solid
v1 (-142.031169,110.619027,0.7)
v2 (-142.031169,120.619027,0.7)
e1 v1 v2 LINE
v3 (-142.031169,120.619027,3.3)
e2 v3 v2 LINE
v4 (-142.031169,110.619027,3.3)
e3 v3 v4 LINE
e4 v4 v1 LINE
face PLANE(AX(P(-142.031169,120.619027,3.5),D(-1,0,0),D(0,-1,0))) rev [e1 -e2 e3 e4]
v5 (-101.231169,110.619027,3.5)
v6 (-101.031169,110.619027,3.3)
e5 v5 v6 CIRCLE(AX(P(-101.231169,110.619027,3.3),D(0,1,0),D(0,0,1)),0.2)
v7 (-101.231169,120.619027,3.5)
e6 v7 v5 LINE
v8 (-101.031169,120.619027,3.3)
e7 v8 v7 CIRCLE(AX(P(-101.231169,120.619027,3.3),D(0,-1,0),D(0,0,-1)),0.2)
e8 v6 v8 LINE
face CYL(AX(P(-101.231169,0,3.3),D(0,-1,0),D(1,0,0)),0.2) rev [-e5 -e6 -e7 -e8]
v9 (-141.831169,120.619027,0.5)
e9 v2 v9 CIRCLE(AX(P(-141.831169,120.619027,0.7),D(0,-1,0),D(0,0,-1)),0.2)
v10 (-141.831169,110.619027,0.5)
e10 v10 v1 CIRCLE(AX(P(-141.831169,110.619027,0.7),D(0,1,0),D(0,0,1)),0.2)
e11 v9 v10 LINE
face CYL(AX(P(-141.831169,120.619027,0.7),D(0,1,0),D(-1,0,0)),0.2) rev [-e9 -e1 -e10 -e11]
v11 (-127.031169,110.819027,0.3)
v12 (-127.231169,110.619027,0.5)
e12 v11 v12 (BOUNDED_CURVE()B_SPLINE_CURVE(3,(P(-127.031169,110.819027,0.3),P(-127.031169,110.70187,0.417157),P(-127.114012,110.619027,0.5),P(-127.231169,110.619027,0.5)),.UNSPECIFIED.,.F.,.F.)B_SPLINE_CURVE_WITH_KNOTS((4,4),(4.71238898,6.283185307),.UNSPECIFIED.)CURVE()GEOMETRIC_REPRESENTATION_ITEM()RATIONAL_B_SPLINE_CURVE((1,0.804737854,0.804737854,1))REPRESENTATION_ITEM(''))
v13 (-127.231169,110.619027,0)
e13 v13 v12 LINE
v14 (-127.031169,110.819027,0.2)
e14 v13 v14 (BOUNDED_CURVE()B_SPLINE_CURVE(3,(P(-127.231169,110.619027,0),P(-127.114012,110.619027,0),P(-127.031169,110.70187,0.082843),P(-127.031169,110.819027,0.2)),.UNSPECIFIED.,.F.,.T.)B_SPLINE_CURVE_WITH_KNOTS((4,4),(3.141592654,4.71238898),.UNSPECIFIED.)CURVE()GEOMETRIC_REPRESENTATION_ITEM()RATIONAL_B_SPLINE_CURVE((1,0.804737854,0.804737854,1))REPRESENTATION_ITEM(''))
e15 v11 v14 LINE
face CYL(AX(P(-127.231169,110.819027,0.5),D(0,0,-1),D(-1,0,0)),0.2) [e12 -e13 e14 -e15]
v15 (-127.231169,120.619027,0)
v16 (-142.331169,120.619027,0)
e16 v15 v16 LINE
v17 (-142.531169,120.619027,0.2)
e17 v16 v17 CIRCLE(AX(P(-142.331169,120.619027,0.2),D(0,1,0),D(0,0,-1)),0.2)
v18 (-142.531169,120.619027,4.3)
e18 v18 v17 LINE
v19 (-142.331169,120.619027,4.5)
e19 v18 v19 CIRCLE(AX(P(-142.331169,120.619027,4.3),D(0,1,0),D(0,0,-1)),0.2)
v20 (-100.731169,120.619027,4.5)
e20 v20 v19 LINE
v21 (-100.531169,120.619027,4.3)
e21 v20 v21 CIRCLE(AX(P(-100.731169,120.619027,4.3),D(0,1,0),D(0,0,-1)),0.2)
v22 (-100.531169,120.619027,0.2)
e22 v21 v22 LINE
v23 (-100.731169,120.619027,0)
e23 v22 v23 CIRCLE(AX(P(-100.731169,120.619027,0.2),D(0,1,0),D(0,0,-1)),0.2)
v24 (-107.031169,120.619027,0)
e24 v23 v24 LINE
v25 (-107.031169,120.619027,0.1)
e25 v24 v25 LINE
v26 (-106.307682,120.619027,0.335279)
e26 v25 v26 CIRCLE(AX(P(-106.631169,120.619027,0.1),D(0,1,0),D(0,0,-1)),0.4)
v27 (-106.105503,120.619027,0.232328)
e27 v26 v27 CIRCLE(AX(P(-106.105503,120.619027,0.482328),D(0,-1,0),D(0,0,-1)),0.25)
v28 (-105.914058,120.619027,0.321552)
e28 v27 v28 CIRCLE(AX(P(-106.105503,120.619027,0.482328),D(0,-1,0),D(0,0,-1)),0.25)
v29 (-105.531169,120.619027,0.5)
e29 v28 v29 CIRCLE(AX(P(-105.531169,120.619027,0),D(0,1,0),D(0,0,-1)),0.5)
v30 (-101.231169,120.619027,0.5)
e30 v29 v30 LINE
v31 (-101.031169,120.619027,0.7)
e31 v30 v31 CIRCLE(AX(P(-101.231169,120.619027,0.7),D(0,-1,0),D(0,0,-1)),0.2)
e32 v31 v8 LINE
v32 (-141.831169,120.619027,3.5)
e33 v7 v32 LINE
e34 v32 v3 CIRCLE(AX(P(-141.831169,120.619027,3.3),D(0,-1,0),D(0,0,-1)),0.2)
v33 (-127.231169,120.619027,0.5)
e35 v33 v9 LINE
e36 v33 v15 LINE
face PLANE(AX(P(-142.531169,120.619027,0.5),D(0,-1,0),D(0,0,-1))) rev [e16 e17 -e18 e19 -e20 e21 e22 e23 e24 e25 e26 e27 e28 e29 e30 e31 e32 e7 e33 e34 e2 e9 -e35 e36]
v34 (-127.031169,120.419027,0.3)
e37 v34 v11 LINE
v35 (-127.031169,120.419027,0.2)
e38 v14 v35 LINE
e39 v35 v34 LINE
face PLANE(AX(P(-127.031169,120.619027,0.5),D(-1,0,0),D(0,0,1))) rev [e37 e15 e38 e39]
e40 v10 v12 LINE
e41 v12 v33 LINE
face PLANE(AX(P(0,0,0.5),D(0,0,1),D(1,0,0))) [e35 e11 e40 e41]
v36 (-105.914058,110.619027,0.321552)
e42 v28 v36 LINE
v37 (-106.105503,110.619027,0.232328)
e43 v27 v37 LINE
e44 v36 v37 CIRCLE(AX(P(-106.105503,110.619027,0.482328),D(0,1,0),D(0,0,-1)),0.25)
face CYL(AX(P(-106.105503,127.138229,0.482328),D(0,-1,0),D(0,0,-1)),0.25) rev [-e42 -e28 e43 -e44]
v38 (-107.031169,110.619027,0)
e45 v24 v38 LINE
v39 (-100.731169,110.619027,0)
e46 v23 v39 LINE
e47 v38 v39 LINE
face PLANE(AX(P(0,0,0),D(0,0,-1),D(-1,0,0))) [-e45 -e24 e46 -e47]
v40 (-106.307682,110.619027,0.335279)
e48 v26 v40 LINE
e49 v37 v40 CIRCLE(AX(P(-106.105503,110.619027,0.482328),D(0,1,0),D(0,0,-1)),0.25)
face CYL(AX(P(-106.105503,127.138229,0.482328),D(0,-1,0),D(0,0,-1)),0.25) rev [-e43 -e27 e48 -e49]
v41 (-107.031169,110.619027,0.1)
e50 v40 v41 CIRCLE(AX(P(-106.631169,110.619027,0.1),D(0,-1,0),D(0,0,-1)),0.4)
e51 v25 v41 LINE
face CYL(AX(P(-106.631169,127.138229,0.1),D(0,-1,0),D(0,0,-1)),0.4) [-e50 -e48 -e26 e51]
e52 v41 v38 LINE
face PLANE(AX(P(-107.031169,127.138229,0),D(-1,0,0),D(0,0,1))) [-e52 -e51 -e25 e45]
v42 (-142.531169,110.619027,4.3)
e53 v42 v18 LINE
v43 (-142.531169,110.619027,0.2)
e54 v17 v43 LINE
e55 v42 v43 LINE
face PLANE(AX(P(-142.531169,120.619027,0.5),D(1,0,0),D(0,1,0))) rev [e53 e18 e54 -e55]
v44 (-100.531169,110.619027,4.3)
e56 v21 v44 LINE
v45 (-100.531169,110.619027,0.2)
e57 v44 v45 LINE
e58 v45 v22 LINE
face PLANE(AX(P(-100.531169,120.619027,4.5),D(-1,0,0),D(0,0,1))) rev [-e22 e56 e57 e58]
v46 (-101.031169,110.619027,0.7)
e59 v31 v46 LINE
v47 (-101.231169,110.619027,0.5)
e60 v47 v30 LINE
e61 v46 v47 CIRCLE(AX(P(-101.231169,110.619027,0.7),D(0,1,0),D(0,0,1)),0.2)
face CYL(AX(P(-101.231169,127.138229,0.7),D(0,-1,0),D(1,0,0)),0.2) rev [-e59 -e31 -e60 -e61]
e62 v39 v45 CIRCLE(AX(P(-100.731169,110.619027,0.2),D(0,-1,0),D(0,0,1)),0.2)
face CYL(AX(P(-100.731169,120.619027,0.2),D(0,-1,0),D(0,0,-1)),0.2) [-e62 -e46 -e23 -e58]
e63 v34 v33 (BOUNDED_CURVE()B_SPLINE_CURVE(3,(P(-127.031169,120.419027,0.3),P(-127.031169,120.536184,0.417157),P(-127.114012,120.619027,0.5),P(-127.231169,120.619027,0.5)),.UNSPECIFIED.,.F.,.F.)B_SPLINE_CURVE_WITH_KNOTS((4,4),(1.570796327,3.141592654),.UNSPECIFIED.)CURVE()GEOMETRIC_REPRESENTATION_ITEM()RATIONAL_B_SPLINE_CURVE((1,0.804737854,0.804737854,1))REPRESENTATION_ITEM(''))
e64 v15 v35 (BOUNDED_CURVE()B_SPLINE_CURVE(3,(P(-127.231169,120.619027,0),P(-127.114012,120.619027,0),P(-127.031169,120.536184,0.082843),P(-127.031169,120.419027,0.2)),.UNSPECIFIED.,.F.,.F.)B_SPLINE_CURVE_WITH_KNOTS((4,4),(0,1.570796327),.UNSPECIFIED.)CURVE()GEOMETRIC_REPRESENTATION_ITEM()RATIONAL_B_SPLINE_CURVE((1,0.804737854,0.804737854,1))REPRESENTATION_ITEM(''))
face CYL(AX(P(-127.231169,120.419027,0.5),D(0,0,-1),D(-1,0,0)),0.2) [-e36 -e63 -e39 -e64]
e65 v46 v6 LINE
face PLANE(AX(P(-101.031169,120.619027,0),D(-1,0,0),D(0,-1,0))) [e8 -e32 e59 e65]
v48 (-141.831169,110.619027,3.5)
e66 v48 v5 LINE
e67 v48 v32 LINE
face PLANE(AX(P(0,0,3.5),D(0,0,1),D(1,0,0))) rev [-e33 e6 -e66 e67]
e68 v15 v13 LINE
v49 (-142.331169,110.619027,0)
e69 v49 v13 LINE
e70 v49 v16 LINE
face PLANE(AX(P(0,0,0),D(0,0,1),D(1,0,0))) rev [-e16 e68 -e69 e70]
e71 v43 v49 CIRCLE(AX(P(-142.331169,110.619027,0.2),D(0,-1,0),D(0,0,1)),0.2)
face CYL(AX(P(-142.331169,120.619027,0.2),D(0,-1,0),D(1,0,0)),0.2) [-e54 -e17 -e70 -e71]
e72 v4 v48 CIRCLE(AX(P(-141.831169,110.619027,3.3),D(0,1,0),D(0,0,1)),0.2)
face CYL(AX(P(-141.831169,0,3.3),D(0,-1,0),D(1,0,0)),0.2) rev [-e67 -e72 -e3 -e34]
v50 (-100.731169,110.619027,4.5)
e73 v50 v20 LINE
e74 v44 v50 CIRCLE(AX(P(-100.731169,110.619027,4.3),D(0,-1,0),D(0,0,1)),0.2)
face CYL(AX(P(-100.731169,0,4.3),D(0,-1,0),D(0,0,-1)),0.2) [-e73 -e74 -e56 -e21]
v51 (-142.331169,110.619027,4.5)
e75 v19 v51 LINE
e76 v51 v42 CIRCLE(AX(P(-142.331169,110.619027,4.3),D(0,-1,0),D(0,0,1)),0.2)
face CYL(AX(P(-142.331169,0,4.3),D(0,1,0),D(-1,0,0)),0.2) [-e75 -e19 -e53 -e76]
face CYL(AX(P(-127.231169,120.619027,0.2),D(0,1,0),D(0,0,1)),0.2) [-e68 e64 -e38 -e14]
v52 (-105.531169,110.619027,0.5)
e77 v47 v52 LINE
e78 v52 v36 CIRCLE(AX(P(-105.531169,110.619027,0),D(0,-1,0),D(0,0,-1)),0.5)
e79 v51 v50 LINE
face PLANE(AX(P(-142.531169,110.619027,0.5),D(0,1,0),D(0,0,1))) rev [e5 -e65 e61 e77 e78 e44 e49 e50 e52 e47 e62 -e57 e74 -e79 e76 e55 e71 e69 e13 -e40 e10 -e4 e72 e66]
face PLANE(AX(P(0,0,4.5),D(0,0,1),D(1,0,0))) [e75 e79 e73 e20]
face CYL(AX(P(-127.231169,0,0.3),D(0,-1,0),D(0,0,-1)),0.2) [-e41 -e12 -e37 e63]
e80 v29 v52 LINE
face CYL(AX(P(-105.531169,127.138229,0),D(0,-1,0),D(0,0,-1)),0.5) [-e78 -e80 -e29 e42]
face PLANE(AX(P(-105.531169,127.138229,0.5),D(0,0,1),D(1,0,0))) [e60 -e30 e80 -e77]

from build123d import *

# Parameters (mm, degrees)
SKETCH1_W           = 15.5
SKETCH1_H           = 10
BOSS_EXTRUDE1_DEPTH = 0.5
SKETCH2_W           = 0.5
SKETCH2_H           = 10
BOSS_EXTRUDE2_DEPTH = 3
SKETCH3_W           = 42
SKETCH3_H           = 10
BOSS_EXTRUDE3_DEPTH = 1
SKETCH4_W           = 0.5
SKETCH4_H           = 10
BOSS_EXTRUDE4_DEPTH = 4.5
BOSS_EXTRUDE5_DEPTH = 10
FILLET1_R           = 0.2


with BuildPart() as part:
    # Sketch1 → Boss-Extrude1 (new body)
    with BuildSketch(Plane.XY):
        with Locations((-134.781169153, 115.619026916)):
            Rectangle(SKETCH1_W, SKETCH1_H)
    extrude(amount=BOSS_EXTRUDE1_DEPTH)

    # Sketch2 → Boss-Extrude2 (add)
    with BuildSketch(Plane.XY.offset(0.5)):
        with Locations((-142.281169153, 115.619026916)):
            Rectangle(SKETCH2_W, SKETCH2_H)
    extrude(amount=BOSS_EXTRUDE2_DEPTH)

    # Sketch3 → Boss-Extrude3 (add)
    with BuildSketch(Plane.XY.offset(3.5)):
        with Locations((-121.531169153, 115.619026916)):
            Rectangle(SKETCH3_W, SKETCH3_H)
    extrude(amount=BOSS_EXTRUDE3_DEPTH)

    # Sketch4 → Boss-Extrude4 (add)
    with BuildSketch(Plane.XY.offset(4.5)):
        with Locations((-100.781169153, 115.619026916)):
            Rectangle(SKETCH4_W, SKETCH4_H)
    extrude(amount=-BOSS_EXTRUDE4_DEPTH)

    # Sketch6 → Boss-Extrude5 (add)
    with BuildSketch(Plane(origin=(0, 110.619026916, 0), x_dir=(-1, 0, 0), z_dir=(0, -1, 0))):
        with BuildLine():
            Line((100.531169153, 0), (107.031169153, 0))
            Line((107.031169153, 0), (107.031169153, -0.1))
            ThreePointArc((107.031169153, -0.1), (106.754872908, -0.48039109), (106.307682248, -0.335279031))
            ThreePointArc((106.307682248, -0.335279031), (106.114215823, -0.2324803), (105.914058339, -0.321552283))
            ThreePointArc((105.914058339, -0.321552283), (105.742384515, -0.453197607), (105.531169153, -0.5))
            Line((105.531169153, -0.5), (100.531169153, -0.5))
            Line((100.531169153, -0.5), (100.531169153, 0))
        make_face()
    extrude(amount=-BOSS_EXTRUDE5_DEPTH)

    # Fillet1
    fillet1_edges = [part.edges().sort_by_distance(p)[0] for p in [
        (-127.031169153, 115.619026916, 0.5),
        (-142.031169153, 115.619026916, 0.5),
        (-142.031169153, 115.619026916, 3.5),
        (-142.531169153, 115.619026916, 4.5),
        (-100.531169153, 115.619026916, 4.5),
        (-100.531169153, 115.619026916, 0),
        (-101.031169153, 115.619026916, 3.5),
        (-127.031169153, 115.619026916, 0),
        (-142.531169153, 115.619026916, 0),
        (-101.031169153, 115.619026916, 0.5),
        (-127.031169153, 120.619026916, 0.25),
        (-127.031169153, 110.619026916, 0.25),
    ]]
    fillet(fillet1_edges, radius=FILLET1_R)


solid = part.part
